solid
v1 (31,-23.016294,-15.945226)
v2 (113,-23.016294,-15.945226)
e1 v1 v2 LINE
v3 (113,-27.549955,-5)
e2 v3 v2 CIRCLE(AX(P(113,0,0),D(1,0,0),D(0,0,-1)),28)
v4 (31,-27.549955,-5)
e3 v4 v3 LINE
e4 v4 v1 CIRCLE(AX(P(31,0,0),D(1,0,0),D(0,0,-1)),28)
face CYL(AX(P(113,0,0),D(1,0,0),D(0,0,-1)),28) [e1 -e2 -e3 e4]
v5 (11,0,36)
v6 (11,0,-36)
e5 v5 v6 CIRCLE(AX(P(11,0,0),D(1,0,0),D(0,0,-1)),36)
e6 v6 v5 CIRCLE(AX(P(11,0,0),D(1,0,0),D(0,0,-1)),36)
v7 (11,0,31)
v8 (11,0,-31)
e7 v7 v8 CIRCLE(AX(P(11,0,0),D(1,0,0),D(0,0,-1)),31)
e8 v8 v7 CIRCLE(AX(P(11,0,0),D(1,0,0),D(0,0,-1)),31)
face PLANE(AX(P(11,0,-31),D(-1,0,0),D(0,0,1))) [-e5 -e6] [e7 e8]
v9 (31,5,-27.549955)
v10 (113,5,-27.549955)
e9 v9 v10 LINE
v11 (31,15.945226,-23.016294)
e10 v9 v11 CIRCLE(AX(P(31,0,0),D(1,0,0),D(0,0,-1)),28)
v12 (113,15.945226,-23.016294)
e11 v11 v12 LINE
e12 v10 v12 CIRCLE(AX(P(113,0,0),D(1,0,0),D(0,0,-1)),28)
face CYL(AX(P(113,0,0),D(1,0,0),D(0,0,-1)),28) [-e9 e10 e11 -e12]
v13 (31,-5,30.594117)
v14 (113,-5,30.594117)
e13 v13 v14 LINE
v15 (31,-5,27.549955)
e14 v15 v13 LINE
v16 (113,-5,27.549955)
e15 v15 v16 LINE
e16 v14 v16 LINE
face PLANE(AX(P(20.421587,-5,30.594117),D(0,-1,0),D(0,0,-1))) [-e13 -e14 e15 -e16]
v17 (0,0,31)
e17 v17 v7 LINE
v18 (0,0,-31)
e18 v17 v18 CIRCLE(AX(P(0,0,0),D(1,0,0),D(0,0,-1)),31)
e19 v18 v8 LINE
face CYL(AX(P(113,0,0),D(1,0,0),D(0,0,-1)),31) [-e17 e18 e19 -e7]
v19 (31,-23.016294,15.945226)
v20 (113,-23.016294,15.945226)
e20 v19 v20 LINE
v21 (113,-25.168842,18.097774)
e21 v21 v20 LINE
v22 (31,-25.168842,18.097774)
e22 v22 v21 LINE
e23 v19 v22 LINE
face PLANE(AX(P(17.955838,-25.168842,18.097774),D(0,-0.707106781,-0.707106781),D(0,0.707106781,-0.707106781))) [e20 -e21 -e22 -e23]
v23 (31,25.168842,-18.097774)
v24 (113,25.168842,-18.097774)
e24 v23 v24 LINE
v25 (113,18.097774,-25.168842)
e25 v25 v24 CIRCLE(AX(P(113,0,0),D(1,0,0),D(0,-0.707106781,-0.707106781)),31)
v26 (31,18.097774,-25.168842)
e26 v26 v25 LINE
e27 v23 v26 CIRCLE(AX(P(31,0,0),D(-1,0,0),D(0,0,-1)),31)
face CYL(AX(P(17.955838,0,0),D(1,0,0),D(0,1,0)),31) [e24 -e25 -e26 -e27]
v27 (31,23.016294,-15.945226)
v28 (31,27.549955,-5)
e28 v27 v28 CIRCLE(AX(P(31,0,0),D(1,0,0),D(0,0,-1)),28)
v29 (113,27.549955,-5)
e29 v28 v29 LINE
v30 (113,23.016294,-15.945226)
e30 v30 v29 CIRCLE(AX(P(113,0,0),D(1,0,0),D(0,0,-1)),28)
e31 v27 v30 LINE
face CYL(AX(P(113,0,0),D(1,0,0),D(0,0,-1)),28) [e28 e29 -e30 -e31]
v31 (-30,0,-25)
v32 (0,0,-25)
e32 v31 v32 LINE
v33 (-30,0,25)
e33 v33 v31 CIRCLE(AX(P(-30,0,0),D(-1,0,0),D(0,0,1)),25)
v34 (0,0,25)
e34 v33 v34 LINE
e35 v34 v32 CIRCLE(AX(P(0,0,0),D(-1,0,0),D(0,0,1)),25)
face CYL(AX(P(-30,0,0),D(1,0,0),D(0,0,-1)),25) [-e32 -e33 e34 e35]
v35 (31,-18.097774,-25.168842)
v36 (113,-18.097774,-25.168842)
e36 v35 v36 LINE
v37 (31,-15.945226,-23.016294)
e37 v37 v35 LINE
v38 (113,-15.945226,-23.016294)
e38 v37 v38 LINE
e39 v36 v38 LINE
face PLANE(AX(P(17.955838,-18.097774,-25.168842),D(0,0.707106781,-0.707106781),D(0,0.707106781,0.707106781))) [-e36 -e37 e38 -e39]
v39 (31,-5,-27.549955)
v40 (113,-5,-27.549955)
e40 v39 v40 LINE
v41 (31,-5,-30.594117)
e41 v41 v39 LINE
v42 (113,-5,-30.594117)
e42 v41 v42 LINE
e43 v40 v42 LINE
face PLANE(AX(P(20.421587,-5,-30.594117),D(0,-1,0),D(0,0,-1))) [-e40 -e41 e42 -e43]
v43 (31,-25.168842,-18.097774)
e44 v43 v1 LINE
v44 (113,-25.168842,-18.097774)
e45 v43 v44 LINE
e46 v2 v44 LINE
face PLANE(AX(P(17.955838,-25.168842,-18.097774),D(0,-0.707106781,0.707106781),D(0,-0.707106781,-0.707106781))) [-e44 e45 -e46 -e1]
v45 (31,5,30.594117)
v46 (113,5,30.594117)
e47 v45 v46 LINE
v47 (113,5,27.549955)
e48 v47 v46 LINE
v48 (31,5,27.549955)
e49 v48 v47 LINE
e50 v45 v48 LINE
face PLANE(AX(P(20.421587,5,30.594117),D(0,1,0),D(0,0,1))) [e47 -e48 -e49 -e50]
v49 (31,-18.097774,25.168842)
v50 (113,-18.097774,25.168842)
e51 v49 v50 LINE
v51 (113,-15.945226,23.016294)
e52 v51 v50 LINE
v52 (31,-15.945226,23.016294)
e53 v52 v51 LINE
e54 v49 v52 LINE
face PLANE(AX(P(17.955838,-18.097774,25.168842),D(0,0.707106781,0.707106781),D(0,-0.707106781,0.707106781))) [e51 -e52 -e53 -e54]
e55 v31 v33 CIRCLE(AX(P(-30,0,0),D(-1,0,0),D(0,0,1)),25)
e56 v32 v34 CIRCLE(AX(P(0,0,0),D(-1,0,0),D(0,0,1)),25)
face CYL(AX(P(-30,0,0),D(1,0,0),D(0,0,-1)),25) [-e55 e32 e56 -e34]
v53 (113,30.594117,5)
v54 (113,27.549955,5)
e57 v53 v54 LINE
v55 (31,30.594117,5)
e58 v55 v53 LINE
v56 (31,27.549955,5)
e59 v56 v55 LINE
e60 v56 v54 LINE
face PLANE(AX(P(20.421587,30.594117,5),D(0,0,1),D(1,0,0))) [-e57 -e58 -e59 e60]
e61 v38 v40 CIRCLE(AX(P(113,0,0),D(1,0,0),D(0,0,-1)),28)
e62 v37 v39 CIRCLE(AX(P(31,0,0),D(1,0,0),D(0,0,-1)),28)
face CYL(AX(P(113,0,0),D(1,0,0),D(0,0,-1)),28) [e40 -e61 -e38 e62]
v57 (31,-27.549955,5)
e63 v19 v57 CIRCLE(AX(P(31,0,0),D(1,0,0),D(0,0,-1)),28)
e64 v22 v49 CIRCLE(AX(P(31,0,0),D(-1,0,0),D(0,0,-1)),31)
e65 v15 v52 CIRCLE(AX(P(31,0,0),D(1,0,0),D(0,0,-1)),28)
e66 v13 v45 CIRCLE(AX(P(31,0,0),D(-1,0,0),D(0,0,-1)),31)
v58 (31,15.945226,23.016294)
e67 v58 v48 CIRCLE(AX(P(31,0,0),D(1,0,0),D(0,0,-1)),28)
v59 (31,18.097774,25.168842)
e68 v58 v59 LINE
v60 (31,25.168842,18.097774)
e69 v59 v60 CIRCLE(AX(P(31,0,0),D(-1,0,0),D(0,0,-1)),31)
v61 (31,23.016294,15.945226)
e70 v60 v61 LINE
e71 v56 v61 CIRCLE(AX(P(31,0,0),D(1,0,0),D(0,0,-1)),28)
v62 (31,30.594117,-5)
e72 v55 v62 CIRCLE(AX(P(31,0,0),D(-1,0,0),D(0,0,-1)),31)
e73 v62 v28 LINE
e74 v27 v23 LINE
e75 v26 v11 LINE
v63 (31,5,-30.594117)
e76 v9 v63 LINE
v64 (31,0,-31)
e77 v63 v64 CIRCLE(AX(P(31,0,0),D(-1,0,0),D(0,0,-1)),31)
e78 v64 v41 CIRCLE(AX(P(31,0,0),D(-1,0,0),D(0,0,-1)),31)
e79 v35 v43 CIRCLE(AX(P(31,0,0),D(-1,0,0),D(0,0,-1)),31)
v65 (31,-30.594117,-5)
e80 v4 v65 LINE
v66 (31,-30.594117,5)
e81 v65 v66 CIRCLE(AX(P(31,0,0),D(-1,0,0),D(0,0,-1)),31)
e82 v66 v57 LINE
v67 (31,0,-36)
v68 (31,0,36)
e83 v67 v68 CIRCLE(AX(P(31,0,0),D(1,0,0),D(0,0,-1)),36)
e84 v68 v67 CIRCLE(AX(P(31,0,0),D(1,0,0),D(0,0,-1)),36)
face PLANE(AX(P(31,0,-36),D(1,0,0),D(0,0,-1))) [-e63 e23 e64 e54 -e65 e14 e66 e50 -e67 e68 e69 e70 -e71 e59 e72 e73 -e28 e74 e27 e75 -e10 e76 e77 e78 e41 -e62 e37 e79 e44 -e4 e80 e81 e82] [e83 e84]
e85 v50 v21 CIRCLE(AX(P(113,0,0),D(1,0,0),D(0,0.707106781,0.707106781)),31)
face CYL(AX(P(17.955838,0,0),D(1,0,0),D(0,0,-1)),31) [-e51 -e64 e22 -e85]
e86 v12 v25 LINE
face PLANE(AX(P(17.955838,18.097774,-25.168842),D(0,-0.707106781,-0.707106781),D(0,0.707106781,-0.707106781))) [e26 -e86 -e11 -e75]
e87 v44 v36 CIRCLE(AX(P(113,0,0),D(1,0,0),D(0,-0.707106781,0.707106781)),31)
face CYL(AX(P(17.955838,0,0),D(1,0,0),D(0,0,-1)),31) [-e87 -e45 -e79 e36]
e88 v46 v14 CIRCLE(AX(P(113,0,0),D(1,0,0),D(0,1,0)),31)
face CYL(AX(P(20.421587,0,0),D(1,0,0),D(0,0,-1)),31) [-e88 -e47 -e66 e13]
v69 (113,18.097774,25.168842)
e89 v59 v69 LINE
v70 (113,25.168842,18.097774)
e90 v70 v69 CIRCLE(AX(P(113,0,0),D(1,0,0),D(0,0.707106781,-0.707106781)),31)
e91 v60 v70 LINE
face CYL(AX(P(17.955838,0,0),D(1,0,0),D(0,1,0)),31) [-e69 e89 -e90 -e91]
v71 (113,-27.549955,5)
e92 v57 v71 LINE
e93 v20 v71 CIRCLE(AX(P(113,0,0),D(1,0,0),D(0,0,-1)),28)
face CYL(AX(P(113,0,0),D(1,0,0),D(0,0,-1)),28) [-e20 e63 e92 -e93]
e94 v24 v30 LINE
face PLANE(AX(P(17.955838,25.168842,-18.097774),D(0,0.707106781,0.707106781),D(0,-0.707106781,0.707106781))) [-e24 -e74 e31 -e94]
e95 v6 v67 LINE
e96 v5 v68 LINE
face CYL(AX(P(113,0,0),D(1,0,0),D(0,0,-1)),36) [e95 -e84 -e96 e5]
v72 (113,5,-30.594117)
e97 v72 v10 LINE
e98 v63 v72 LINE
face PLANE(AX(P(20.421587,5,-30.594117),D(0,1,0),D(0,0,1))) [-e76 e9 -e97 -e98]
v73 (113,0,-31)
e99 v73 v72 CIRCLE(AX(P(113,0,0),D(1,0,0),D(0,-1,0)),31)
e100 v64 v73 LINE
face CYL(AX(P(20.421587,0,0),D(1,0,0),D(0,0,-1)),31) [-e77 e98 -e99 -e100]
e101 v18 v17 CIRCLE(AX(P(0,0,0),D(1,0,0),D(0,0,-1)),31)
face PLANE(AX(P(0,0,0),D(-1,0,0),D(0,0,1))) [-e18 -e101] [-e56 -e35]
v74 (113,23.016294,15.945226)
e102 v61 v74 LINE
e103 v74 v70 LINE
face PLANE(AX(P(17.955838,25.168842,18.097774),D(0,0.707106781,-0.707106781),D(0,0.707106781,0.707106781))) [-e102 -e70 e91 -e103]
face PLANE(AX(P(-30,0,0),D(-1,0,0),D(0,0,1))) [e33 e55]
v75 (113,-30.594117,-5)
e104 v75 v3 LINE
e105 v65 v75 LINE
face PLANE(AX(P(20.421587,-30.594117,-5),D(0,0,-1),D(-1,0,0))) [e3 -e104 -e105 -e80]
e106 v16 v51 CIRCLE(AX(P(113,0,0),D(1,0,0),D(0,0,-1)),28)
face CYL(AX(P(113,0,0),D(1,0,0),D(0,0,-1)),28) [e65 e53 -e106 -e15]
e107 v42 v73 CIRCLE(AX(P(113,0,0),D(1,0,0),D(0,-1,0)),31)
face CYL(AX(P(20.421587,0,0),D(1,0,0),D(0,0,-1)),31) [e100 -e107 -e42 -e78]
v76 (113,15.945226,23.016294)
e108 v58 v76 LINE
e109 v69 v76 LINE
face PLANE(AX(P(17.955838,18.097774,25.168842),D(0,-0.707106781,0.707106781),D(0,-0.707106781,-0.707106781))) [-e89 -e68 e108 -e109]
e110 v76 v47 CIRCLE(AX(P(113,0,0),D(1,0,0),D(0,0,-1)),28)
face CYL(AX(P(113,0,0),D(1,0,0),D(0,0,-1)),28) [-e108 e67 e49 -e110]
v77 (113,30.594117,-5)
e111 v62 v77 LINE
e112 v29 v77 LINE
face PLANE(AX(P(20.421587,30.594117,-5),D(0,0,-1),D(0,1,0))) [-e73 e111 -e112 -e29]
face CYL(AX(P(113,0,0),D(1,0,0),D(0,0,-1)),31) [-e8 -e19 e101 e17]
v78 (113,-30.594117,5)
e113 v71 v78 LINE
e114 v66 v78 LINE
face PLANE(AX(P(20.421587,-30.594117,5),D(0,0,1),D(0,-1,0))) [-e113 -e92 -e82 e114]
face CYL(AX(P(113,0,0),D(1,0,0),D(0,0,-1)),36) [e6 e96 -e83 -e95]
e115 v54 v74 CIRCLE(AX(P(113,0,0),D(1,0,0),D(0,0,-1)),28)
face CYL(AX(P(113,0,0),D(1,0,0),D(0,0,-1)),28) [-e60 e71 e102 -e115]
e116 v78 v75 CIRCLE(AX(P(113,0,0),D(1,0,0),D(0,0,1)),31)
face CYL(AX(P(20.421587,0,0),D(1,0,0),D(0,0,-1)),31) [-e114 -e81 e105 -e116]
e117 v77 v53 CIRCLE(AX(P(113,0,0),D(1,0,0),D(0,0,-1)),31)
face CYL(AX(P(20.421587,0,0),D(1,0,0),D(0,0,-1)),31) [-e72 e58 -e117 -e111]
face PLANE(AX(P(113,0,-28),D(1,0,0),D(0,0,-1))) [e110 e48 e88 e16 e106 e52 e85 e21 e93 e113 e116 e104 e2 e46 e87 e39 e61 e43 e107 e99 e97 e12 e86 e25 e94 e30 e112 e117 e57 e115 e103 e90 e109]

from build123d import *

# Parameters (mm, degrees)
BOSS_EXTRUDE1_DEPTH = 82
CIRPATTERN1_COUNT   = 8
SKETCH3_R           = 25
BOSS_EXTRUDE2_DEPTH = 30


with BuildPart() as part:
    # Sketch1 → Revolve1 (revolve)
    with BuildSketch(Plane(origin=(0, 0, 0), x_dir=(1, 0, 0), z_dir=(0, 1, 0))):
        Polygon((0, 0), (0, 31), (11, 31), (11, 36), (31, 36), (31, 28), (113, 28), (113, 0), align=None)
    revolve(axis=Axis((113, 0, 0), (-1, 0, 0)))

    # Sketch2 → Boss-Extrude1 (add)
    with BuildSketch(Plane(origin=(113, 0, 0), x_dir=(0, 0, -1), z_dir=(1, 0, 0))):
        with BuildLine():
            Line((-5, 30.594117082), (-5, 27.549954628))
            ThreePointArc((-5, 27.549954628), (0, 28), (5, 27.549954628))
            Line((5, 27.549954628), (5, 30.594117082))
            ThreePointArc((5, 30.594117082), (0, 31), (-5, 30.594117082))
        make_face()
    boss_extrude1 = extrude(amount=-BOSS_EXTRUDE1_DEPTH)

    # CirPattern1: Boss-Extrude1 ×8 about axis
    cirpattern1_axis = Axis((0, 0, 0), (1, 0, 0))
    for i in range(1, CIRPATTERN1_COUNT):
        add(boss_extrude1.rotate(cirpattern1_axis, i * 360 / CIRPATTERN1_COUNT))

    # Sketch3 → Boss-Extrude2 (add)
    with BuildSketch(Plane.ZY):
        Circle(SKETCH3_R)
    extrude(amount=BOSS_EXTRUDE2_DEPTH)


solid = part.part
